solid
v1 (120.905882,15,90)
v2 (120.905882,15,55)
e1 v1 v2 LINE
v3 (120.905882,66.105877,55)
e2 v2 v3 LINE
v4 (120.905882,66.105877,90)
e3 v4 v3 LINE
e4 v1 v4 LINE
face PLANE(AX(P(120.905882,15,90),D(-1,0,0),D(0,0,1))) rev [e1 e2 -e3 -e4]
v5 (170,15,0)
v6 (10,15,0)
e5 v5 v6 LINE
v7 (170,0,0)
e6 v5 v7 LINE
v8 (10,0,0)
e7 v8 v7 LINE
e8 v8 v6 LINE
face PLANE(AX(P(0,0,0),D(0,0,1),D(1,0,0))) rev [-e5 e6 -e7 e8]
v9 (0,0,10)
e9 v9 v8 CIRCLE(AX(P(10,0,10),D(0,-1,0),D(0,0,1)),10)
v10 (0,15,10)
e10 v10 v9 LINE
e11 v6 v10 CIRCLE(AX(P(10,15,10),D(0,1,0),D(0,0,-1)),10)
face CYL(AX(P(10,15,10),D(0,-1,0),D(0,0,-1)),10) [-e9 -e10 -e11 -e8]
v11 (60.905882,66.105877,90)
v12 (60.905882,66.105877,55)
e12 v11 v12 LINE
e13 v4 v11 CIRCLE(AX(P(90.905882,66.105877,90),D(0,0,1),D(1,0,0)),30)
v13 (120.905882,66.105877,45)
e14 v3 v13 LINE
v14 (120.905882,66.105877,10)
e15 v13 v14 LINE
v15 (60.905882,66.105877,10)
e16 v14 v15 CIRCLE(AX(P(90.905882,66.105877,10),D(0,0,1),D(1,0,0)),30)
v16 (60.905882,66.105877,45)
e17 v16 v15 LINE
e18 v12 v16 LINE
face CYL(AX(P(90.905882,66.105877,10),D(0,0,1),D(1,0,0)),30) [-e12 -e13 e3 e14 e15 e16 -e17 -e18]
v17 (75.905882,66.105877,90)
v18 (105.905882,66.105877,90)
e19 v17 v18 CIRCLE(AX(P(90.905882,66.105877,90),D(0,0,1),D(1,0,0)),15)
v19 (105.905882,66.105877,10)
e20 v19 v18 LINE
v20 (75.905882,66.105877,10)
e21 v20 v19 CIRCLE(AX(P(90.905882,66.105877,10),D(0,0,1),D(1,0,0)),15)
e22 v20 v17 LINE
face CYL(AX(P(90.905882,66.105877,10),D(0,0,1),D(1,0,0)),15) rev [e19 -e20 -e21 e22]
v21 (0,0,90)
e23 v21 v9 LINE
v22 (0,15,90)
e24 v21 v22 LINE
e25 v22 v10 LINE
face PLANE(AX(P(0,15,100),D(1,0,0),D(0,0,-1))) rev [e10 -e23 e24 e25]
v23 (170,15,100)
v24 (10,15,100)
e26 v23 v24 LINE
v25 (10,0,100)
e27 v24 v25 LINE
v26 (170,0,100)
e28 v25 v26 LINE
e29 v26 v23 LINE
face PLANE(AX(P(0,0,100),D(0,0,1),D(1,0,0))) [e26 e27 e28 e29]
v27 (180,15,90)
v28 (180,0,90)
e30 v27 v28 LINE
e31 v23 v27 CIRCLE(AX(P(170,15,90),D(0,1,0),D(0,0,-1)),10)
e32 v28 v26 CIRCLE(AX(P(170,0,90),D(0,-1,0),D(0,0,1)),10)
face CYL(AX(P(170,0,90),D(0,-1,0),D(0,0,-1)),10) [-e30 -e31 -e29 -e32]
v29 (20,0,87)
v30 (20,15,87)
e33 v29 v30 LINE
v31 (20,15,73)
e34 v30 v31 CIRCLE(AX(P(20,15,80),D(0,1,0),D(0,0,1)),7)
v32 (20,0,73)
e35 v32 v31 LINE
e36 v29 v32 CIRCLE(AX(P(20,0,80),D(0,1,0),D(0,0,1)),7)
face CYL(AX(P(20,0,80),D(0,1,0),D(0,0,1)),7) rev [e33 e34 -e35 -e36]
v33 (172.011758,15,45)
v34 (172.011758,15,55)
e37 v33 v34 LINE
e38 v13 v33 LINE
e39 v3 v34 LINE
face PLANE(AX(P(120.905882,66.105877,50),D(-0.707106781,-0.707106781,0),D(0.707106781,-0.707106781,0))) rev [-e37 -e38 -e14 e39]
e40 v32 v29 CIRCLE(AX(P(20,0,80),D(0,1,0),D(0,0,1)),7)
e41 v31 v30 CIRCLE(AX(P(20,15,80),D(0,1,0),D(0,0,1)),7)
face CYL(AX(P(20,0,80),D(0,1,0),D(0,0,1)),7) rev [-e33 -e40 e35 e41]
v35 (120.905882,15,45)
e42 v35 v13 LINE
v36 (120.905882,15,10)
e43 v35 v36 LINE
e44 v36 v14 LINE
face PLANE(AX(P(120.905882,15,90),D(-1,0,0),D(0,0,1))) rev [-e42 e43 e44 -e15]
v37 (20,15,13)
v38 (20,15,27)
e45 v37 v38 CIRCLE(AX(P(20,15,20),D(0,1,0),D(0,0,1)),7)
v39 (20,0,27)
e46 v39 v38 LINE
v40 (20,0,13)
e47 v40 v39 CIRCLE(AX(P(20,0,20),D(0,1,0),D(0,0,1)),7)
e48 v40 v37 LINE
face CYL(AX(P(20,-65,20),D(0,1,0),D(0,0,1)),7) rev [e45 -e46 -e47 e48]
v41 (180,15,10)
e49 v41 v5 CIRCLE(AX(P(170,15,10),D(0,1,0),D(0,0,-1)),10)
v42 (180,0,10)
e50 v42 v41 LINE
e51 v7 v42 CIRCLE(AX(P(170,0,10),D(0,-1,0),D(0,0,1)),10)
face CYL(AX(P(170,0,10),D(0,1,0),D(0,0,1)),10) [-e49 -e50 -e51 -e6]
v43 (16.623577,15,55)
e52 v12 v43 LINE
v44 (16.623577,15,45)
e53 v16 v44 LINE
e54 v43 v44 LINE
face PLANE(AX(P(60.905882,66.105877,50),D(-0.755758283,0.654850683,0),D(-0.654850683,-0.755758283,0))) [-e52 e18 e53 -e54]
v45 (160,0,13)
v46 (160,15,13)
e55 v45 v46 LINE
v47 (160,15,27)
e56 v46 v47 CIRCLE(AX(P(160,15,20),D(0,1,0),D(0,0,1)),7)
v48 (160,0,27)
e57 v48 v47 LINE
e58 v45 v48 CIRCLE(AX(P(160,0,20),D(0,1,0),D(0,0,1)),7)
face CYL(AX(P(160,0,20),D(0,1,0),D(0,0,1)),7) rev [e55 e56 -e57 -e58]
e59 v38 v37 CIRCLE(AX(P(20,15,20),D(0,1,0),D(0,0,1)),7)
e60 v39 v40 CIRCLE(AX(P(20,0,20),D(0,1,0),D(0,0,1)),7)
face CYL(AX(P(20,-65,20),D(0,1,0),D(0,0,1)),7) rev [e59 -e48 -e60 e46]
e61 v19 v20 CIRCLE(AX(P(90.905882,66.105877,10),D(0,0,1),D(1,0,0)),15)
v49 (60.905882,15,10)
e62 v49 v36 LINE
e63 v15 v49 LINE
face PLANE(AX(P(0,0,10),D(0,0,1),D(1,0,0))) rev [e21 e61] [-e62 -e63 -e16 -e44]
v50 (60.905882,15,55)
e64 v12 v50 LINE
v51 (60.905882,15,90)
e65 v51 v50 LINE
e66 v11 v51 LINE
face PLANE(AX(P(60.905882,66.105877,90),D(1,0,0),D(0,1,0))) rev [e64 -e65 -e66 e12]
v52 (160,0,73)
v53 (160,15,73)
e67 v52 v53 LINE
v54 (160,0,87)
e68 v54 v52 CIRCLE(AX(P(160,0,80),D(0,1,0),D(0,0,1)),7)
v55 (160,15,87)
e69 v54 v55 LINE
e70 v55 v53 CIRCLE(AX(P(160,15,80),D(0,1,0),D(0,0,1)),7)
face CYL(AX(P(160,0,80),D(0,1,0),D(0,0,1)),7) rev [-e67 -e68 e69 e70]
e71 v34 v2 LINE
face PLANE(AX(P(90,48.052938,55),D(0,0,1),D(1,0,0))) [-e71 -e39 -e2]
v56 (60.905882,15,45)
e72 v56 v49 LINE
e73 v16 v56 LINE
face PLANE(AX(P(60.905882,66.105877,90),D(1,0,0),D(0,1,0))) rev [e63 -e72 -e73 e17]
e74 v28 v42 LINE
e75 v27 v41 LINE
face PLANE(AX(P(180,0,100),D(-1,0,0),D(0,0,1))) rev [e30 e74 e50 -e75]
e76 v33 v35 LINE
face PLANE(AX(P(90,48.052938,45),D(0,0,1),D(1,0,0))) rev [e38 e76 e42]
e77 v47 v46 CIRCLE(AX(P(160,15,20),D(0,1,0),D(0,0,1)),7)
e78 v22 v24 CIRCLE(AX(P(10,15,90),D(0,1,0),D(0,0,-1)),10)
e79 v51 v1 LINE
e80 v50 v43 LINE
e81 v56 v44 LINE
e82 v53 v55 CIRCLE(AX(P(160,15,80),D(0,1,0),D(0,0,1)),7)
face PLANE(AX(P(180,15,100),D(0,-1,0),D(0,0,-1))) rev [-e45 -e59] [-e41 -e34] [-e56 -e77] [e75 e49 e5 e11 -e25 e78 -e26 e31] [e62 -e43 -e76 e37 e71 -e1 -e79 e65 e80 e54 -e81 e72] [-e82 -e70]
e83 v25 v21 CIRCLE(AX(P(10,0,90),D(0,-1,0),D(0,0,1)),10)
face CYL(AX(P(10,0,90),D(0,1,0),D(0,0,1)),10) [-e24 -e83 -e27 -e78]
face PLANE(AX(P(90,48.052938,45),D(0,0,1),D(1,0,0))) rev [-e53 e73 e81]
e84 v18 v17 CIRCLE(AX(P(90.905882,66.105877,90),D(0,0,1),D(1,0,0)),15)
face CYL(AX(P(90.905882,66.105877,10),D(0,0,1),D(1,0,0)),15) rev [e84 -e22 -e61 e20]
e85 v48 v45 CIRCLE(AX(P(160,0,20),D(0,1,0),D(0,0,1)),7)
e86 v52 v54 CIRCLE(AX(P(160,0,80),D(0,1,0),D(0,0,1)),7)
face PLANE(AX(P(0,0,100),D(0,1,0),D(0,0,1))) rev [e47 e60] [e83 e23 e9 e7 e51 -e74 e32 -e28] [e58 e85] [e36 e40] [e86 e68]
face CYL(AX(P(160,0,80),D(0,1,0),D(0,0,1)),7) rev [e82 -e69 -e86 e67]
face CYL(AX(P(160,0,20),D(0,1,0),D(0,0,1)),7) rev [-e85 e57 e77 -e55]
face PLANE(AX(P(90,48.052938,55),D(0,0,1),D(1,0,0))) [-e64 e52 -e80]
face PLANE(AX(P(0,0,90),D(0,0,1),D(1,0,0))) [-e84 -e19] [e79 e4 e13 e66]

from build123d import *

# Parameters (mm, degrees)
BASE_PLATE_SKETCH_W             = 180
BASE_PLATE_SKETCH_H             = 15
BASE_PLATE_DEPTH                = 100
BEARING_UPRIGHT_SKETCH_R        = 30
BEARING_UPRIGHT_SKETCH_R_2      = 15
BEARING_UPRIGHT_DEPTH           = 40
UPRIGHT_BLOCK_SKETCH_W          = 60
UPRIGHT_BLOCK_SKETCH_H          = 51.105876717
UPRIGHT_BLOCK_DEPTH             = 40
BEARING_START                   = -80
BEARING_BORE_SKETCH_R           = 15
BEARING_BORE_DEPTH              = 80
SUPPORT_RIB_A_REACH             = 212.087
SUPPORT_RIB_A_SKETCH_WALL_W     = 492.173009792
SUPPORT_RIB_A_SKETCH_WALL_H     = 10
SUPPORT_RIB_B_REACH             = 212.087
SUPPORT_RIB_B_SKETCH_WALL_W     = 492.173009792
SUPPORT_RIB_B_SKETCH_WALL_H     = 10
BASE_PLATE_CUT_A_SKETCH_R       = 7
BASE_PLATE_CUT_A_DEPTH          = 80
BASE_PLATE_CUT_B_SKETCH_R       = 7
BASE_PLATE_CUT_B_DEPTH          = 222.310106498
BASE_PLATE_CORNER_FILLETS_R10_R = 10


with BuildPart() as part:
    # Base Plate Sketch → Base Plate (new body)
    with BuildSketch(Plane.XY):
        with Locations((90, 7.5)):
            Rectangle(BASE_PLATE_SKETCH_W, BASE_PLATE_SKETCH_H)
    extrude(amount=BASE_PLATE_DEPTH)



with BuildPart() as body_2:
    # Bearing Upright Sketch → Bearing Upright (new, symmetric)
    with BuildSketch(Plane.XY.offset(50)):
        with Locations((90.90588176, 66.105876717)):
            Circle(BEARING_UPRIGHT_SKETCH_R)
        with Locations((90.90588176, 66.105876717)):
            Circle(BEARING_UPRIGHT_SKETCH_R_2, mode=Mode.SUBTRACT)
    extrude(amount=BEARING_UPRIGHT_DEPTH, both=True)


with BuildPart() as part_1:
    add(part.part)

    add(body_2.part)  # Upright Block merges body 2
    # Upright Block Sketch → Upright Block (add, symmetric)
    with BuildSketch(Plane.XY.offset(50)):
        with Locations((90.90588176, 40.552938359)):
            Rectangle(UPRIGHT_BLOCK_SKETCH_W, UPRIGHT_BLOCK_SKETCH_H)
    extrude(amount=UPRIGHT_BLOCK_DEPTH, both=True)

    # Bearing Bore Sketch → Bearing Bore (cut)
    with BuildSketch(Plane.XY.offset(90).offset(BEARING_START)):
        with Locations((90.90588176, 66.105876717)):
            Circle(BEARING_BORE_SKETCH_R)
    extrude(amount=BEARING_BORE_DEPTH, mode=Mode.SUBTRACT)

    # Support Rib A Sketch wall → Support Rib A (add, up to next)
    with BuildSketch(Plane(origin=(37.986107853, 39.654336798, 50), x_dir=(-0.654850683055, -0.755758283383, 0), z_dir=(0.755758283383, -0.654850683055, 0)), mode=Mode.PRIVATE) as support_rib_a_sk1:
        Rectangle(SUPPORT_RIB_A_SKETCH_WALL_W, SUPPORT_RIB_A_SKETCH_WALL_H)
    support_rib_a_tool1 = extrude(support_rib_a_sk1.sketch, amount=SUPPORT_RIB_A_REACH, mode=Mode.PRIVATE) - part_1.part
    add(support_rib_a_tool1.solids().sort_by_distance((37.986107853, 39.654336798, 50))[0])

    # Support Rib B Sketch wall → Support Rib B (add, up to next)
    with BuildSketch(Plane(origin=(145.654619102, 41.357139375, 50), x_dir=(0.707106781187, -0.707106781187, 0), z_dir=(0.707106781187, 0.707106781187, 0)), mode=Mode.PRIVATE) as support_rib_b_sk1:
        Rectangle(SUPPORT_RIB_B_SKETCH_WALL_W, SUPPORT_RIB_B_SKETCH_WALL_H)
    support_rib_b_tool1 = extrude(support_rib_b_sk1.sketch, amount=-SUPPORT_RIB_B_REACH, mode=Mode.PRIVATE) - part_1.part
    add(support_rib_b_tool1.solids().sort_by_distance((145.654619102, 41.357139375, 50))[0])

    # Base Plate Cut A Sketch → Base Plate Cut A (cut)
    with BuildSketch(Plane(origin=(0, 15, 0), x_dir=(1, 0, 0), z_dir=(0, 1, 0))):
        with Locations(Location((20, -20, 0), (0, 0, 270))):
            Circle(BASE_PLATE_CUT_A_SKETCH_R)
    extrude(amount=-BASE_PLATE_CUT_A_DEPTH, mode=Mode.SUBTRACT)

    # Base Plate Cut B Sketch → Base Plate Cut B (cut, through all)
    with BuildSketch(Plane(origin=(0, 15, 0), x_dir=(1, 0, 0), z_dir=(0, 1, 0))):
        with Locations(Location((160, -20, 0), (0, 0, 270))):
            Circle(BASE_PLATE_CUT_B_SKETCH_R)
        with Locations(Location((160, -80, 0), (0, 0, 270))):
            Circle(BASE_PLATE_CUT_B_SKETCH_R)
        with Locations(Location((20, -80, 0), (0, 0, 270))):
            Circle(BASE_PLATE_CUT_B_SKETCH_R)
    extrude(amount=-BASE_PLATE_CUT_B_DEPTH, mode=Mode.SUBTRACT)

    # Base Plate Corner Fillets R10
    base_plate_corner_fillets_r10_edges = [part_1.edges().sort_by_distance(p)[0] for p in [
        (180, 7.5, 100),
        (0, 7.5, 100),
        (180, 7.5, 0),
        (0, 7.5, 0),
    ]]
    fillet(base_plate_corner_fillets_r10_edges, radius=BASE_PLATE_CORNER_FILLETS_R10_R)


solid = part_1.part
